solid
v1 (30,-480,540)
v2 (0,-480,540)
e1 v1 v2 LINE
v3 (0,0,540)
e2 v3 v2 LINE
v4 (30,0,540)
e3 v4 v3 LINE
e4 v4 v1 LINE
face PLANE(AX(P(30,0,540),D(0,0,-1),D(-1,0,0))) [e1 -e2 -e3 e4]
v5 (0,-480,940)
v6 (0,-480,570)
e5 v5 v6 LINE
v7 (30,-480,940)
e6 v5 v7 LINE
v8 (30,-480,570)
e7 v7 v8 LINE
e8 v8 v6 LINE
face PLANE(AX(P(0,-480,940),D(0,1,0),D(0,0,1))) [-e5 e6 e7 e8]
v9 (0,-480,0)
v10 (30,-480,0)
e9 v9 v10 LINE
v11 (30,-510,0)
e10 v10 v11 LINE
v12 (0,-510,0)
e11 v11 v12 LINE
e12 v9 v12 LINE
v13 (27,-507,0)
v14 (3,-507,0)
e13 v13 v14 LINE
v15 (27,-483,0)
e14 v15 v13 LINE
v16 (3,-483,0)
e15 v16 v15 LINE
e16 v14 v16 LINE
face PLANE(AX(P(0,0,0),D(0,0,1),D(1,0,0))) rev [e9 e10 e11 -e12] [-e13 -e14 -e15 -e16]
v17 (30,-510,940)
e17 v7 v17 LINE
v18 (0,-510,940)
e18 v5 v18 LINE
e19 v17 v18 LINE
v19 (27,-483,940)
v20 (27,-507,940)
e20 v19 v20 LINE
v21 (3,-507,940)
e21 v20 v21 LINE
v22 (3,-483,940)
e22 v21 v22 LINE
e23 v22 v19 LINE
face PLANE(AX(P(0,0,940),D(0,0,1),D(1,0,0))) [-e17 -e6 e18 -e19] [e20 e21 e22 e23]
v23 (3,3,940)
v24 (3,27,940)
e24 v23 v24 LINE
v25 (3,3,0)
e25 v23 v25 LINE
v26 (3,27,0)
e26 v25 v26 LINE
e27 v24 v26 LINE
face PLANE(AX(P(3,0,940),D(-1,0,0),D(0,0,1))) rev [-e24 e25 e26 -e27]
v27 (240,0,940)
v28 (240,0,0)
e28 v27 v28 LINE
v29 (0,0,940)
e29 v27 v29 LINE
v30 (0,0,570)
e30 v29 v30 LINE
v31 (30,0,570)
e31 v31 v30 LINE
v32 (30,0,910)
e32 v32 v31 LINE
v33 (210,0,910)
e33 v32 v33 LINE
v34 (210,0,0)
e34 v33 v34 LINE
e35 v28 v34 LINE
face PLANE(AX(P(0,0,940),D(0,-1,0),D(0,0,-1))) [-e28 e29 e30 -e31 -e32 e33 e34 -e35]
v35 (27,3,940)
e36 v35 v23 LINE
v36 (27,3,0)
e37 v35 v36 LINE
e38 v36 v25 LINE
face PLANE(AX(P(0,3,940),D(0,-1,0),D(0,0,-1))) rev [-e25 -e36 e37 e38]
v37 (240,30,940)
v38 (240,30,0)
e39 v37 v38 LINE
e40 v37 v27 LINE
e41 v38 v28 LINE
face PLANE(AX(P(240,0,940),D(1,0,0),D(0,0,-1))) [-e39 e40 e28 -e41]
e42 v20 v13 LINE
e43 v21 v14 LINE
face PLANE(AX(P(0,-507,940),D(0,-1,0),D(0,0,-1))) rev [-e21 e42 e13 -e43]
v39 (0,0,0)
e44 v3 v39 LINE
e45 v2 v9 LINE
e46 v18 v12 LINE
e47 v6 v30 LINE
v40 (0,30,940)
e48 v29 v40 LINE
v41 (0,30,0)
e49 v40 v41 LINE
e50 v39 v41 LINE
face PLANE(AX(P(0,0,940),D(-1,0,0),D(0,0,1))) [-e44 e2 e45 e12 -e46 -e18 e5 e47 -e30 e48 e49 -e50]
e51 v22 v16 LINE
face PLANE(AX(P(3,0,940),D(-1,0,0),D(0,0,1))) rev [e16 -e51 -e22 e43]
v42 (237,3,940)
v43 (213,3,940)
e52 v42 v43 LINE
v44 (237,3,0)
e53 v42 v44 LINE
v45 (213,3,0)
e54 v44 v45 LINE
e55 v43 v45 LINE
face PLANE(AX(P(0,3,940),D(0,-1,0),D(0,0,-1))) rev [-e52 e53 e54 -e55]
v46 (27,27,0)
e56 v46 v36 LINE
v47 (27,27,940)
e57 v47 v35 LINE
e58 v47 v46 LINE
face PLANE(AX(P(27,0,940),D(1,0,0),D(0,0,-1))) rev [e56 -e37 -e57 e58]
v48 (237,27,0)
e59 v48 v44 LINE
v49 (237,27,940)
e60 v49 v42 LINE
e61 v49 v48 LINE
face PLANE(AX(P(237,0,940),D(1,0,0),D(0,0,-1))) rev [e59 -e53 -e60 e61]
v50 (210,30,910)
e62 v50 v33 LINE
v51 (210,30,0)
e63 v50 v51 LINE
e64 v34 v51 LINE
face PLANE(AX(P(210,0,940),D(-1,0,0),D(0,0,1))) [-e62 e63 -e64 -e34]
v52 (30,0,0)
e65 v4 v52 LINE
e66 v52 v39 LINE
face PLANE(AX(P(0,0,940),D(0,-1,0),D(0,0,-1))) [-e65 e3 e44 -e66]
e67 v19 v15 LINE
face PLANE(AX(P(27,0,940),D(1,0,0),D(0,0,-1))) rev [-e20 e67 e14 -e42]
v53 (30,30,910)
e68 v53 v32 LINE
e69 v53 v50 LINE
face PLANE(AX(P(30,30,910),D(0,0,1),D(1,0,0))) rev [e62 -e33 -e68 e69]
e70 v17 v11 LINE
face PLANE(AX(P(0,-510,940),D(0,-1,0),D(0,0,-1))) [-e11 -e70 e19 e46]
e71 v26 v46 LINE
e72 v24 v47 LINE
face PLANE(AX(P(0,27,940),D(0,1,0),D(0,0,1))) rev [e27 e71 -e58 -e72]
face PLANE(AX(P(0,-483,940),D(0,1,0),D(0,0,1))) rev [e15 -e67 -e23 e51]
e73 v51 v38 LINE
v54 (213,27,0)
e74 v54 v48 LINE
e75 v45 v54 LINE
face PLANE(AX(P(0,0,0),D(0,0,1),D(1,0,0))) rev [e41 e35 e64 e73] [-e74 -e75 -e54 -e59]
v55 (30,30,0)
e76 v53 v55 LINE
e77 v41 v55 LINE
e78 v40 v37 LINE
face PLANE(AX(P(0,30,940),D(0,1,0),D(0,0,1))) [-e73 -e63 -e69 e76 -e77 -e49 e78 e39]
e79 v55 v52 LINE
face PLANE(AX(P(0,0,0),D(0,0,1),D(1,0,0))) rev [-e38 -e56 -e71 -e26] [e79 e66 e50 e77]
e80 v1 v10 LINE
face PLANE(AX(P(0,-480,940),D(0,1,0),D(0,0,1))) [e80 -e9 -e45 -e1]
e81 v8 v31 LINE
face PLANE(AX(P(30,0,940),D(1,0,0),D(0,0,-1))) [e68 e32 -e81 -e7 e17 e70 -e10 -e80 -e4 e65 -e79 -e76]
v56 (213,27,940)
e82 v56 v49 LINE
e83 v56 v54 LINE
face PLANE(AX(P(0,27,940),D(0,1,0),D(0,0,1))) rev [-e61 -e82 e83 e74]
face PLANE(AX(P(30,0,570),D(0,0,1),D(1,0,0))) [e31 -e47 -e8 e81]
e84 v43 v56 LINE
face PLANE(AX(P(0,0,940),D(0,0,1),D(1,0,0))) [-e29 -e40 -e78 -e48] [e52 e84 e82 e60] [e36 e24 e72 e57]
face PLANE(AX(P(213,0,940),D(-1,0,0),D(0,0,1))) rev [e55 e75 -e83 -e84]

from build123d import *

# Parameters (mm, degrees)
SKETCH_1_W          = 30
SKETCH_1_H          = 30
SKETCH_1_W_2        = 24
SKETCH_1_H_2        = 24
EXTRUDE_1_DEPTH     = 940
EXTRUDE_1_2_DEPTH   = 940
EXTRUDE_1_3_DEPTH   = 940
SKETCH_3_W          = 30
SKETCH_3_H          = 30
SKETCH_3_W_2        = 24
SKETCH_3_H_2        = 24
EXTRUDE_2_DEPTH     = 480
SKETCH_4_W          = 30
SKETCH_4_H          = 480
CUT_EXTRUDE_1_DEPTH = 37
SKETCH_5_W          = 30
SKETCH_5_H          = 480
EXTRUDE_3_DEPTH     = 30
SKETCH_6_W          = 30
SKETCH_6_H          = 30
EXTRUDE_4_DEPTH     = 180


with BuildPart() as part:
    # 草图1 → 凸台-拉伸1 (new body)
    with BuildSketch(Plane.XY):
        with Locations((15, 15)):
            Rectangle(SKETCH_1_W, SKETCH_1_H)
        with Locations((15, 15)):
            Rectangle(SKETCH_1_W_2, SKETCH_1_H_2, mode=Mode.SUBTRACT)
    extrude(amount=EXTRUDE_1_DEPTH)



with BuildPart() as body_2:
    # 草图1 → Extrude 1 2 (new body)
    with BuildSketch(Plane.XY):
        with Locations((225, 15)):
            Rectangle(SKETCH_1_W, SKETCH_1_H)
        with Locations((225, 15)):
            Rectangle(SKETCH_1_W_2, SKETCH_1_H_2, mode=Mode.SUBTRACT)
    extrude(amount=EXTRUDE_1_2_DEPTH)



with BuildPart() as body_3:
    # 草图1 → Extrude 1 3 (new body)
    with BuildSketch(Plane.XY):
        with Locations((15, -495)):
            Rectangle(SKETCH_1_W, SKETCH_1_H)
        with Locations((15, -495)):
            Rectangle(SKETCH_1_W_2, SKETCH_1_H_2, mode=Mode.SUBTRACT)
    extrude(amount=EXTRUDE_1_3_DEPTH)


with BuildPart() as part_1:
    add(part.part)

    add(body_3.part)  # 凸台-拉伸2 merges body 3
    # 草图3 → 凸台-拉伸2 (add)
    with BuildSketch(Plane.XZ):
        with Locations((15, 385)):
            Rectangle(SKETCH_3_W, SKETCH_3_H)
        with Locations((15, 385)):
            Rectangle(SKETCH_3_W_2, SKETCH_3_H_2, mode=Mode.SUBTRACT)
    extrude(amount=EXTRUDE_2_DEPTH)

    # 草图4 → 切除-拉伸1 (cut)
    with BuildSketch(Plane.ZY):
        with Locations((385, -240)):
            Rectangle(SKETCH_4_W, SKETCH_4_H)
    extrude(amount=-CUT_EXTRUDE_1_DEPTH, mode=Mode.SUBTRACT)


with BuildPart() as cut_extrude_1_piece_1:
    # of the separate pieces the step leaves, piece 1, a body of its own (cut_extrude_1_pieces)
    add(part_1.part.solids().sort_by_distance((0, 0, 940))[0])



with BuildPart() as cut_extrude_1_piece_2:
    # of the separate pieces the step leaves, piece 2, a body of its own (cut_extrude_1_pieces)
    add(part_1.part.solids().sort_by_distance((0, -510, 0))[0])


with BuildPart() as cut_extrude_1_piece_1_1:
    add(cut_extrude_1_piece_1.part)

    add(cut_extrude_1_piece_2.part)  # 凸台-拉伸3 merges 切除-拉伸1 piece 2
    # 草图5 → 凸台-拉伸3 (add)
    with BuildSketch(Plane.ZY):
        with Locations((555, -240)):
            Rectangle(SKETCH_5_W, SKETCH_5_H)
    extrude(amount=-EXTRUDE_3_DEPTH)


with BuildPart() as body_2_1:
    add(body_2.part)

    add(cut_extrude_1_piece_1_1.part)  # 凸台-拉伸4 merges 切除-拉伸1 piece 1
    # 草图6 → 凸台-拉伸4 (add)
    with BuildSketch(Plane.ZY.offset(-210)):
        with Locations((925, 15)):
            Rectangle(SKETCH_6_W, SKETCH_6_H)
    extrude(amount=EXTRUDE_4_DEPTH)


solid = body_2_1.part
